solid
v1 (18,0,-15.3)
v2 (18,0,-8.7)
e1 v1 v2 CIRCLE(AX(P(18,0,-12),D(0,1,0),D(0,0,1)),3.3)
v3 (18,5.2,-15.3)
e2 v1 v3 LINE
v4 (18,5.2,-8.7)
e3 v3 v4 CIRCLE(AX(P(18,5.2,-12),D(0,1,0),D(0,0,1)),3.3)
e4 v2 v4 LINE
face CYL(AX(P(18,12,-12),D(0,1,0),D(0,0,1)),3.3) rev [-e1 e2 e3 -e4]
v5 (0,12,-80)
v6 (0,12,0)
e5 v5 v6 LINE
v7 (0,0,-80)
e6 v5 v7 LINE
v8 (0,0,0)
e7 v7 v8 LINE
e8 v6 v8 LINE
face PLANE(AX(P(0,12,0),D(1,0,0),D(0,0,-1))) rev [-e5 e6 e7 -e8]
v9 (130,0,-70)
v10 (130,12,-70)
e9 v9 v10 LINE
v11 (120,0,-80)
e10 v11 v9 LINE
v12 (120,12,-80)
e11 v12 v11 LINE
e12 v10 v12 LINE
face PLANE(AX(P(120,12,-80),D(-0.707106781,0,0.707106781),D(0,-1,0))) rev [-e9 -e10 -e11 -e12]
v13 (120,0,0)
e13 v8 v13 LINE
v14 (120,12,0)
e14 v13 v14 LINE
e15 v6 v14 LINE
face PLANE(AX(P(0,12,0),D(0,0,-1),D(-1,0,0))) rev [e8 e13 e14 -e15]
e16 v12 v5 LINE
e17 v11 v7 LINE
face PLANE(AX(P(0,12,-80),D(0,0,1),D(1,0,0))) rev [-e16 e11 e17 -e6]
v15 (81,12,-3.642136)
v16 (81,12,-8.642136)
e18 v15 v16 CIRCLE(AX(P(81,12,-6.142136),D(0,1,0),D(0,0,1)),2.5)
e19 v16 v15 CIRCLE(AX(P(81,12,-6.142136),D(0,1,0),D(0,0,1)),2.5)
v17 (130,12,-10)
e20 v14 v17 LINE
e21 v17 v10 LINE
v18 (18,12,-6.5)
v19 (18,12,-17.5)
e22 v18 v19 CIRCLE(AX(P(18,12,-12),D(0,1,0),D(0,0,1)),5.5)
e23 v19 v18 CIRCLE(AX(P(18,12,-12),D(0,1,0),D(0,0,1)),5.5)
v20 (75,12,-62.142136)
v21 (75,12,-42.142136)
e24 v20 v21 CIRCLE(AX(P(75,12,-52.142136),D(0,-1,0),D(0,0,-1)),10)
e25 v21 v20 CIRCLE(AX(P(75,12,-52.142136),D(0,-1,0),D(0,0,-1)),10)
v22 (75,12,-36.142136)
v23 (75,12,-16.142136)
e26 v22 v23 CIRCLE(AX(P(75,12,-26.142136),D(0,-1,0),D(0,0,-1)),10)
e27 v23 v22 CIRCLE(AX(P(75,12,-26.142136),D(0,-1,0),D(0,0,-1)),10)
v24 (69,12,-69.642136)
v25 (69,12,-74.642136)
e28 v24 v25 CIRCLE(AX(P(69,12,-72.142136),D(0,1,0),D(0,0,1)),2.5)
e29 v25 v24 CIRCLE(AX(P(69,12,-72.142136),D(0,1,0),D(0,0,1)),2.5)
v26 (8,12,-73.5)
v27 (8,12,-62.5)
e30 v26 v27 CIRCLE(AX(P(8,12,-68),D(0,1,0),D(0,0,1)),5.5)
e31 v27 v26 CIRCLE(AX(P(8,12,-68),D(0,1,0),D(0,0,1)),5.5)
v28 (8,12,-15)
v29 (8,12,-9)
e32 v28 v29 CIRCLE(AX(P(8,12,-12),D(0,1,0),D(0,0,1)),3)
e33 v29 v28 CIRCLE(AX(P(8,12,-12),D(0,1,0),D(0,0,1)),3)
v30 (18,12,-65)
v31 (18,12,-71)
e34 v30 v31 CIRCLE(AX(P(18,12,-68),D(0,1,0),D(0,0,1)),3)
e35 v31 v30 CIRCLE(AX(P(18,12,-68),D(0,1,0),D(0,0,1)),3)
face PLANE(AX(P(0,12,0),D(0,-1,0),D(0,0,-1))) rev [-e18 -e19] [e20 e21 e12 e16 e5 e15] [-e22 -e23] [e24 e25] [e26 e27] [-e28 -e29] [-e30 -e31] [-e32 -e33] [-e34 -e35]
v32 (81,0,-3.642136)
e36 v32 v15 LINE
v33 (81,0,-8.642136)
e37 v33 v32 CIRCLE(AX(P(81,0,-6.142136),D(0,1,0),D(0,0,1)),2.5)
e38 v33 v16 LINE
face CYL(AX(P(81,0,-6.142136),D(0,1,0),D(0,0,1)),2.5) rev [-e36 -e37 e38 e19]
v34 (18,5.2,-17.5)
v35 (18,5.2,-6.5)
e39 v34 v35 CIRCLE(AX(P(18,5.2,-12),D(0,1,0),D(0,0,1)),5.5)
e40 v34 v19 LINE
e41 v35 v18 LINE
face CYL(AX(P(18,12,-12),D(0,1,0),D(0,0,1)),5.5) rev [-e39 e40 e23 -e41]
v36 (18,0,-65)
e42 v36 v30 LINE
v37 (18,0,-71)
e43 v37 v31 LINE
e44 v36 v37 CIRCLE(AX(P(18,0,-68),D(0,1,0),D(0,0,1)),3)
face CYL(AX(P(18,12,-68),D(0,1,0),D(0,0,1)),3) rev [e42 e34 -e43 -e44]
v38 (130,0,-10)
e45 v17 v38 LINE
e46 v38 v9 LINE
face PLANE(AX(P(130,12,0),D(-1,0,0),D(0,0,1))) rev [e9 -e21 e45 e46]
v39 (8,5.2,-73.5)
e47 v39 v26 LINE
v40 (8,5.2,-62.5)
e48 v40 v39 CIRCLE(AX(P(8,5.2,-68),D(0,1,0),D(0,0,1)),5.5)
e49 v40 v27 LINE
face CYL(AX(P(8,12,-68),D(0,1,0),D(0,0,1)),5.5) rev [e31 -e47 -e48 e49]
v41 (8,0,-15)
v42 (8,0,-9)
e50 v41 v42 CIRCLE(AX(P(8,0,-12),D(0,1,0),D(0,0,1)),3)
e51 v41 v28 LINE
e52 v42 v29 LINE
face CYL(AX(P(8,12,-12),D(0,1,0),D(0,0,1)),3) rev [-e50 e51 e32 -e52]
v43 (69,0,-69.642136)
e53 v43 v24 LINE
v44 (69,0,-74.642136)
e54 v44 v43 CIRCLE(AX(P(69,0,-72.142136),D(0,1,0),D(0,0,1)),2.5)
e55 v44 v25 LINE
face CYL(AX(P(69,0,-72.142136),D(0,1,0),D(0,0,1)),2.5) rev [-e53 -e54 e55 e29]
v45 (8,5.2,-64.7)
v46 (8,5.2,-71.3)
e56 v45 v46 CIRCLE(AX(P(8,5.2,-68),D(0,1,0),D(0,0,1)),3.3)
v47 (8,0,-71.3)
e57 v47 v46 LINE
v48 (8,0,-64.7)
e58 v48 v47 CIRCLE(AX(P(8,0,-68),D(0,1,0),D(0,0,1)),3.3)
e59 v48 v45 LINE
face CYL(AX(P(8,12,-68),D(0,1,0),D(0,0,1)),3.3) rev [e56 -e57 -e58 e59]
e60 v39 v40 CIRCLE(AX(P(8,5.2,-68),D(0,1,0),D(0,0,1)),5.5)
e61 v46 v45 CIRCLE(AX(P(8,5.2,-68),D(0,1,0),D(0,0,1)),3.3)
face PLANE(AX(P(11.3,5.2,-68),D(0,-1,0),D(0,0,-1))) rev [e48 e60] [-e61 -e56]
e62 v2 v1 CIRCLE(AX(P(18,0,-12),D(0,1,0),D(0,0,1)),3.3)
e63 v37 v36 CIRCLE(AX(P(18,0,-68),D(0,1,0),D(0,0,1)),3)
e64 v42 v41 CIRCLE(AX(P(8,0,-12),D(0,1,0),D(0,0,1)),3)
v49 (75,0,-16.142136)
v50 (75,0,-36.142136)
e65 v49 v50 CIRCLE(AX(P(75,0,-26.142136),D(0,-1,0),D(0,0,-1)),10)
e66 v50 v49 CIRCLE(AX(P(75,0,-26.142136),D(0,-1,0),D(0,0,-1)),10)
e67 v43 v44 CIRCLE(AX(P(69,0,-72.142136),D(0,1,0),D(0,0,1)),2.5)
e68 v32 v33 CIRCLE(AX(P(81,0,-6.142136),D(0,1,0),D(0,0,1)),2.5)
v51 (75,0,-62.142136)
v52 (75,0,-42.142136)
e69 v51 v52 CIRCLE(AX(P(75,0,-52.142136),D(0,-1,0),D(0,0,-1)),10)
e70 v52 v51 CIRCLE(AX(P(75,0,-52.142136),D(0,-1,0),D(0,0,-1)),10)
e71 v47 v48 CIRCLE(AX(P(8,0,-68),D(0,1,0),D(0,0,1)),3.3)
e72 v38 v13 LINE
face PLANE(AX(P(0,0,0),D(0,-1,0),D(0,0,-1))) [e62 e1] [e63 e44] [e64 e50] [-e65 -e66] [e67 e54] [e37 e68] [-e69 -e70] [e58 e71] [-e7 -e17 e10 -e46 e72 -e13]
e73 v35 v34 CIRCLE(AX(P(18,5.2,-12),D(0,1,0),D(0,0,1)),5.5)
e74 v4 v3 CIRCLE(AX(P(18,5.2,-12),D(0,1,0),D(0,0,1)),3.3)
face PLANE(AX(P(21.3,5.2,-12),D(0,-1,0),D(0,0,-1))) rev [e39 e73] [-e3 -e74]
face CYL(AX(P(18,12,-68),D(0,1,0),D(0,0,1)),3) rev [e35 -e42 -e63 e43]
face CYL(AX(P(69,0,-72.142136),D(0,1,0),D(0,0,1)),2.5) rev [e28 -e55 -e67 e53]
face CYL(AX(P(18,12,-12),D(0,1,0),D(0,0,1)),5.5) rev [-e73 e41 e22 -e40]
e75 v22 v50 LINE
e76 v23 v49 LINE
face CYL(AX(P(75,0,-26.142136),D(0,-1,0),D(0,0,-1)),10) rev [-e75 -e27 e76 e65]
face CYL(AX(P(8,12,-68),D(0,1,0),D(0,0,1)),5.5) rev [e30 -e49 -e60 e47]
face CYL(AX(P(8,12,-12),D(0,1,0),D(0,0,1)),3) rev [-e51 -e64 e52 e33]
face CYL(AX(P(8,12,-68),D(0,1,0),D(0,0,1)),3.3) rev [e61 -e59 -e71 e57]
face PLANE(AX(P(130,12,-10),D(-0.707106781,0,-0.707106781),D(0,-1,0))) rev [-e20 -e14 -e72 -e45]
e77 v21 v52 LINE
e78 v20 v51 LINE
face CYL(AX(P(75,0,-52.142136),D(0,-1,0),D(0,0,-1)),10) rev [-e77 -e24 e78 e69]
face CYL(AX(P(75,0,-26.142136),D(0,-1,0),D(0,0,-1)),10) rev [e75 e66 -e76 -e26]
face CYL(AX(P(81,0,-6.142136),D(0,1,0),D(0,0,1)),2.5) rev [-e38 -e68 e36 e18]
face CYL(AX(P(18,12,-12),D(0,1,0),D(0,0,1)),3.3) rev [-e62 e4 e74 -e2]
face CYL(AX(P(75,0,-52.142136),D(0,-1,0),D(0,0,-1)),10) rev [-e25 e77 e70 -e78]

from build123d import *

# Parameters (mm, degrees)
SKETCH1_W                                            = 130
SKETCH1_H                                            = 80
BOSS_EXTRUDE1_DEPTH                                  = 12
CHAMFER1_SIZE                                        = 10
CBORE_FOR_M6_HEXAGON_SOCKET_HEAD_CAP_SCR_D           = 6.6
CBORE_FOR_M6_HEXAGON_SOCKET_HEAD_CAP_SCR_CBORE_D     = 11
CBORE_FOR_M6_HEXAGON_SOCKET_HEAD_CAP_SCR_CBORE_DEPTH = 6.8
F_6_0MM_DOWEL_HOLE_1_D                               = 6
F_20_0MM_DOWEL_HOLE_1_D                              = 20
SKETCH17_R                                           = 2.5
CUT_EXTRUDE1_DEPTH                                   = 154.114336363


with BuildPart() as part:
    # Sketch1 → Boss-Extrude1 (new body)
    with BuildSketch(Plane(origin=(0, 0, 0), x_dir=(1, 0, 0), z_dir=(0, 1, 0))):
        with Locations((65, 40)):
            Rectangle(SKETCH1_W, SKETCH1_H)
    extrude(amount=BOSS_EXTRUDE1_DEPTH)

    # Chamfer1
    chamfer1_edges = [part.edges().sort_by_distance(p)[0] for p in [
        (130, 6, -80),
        (130, 6, 0),
    ]]
    chamfer(chamfer1_edges, length=CHAMFER1_SIZE)

    # CBORE for M6 Hexagon socket head cap screws1 (through all)
    with Locations(Plane(origin=(8, 12, -68), x_dir=(0, 0, 1), z_dir=(0, 1, 0))):
        with Locations((0, 0), (56, 10)):
            CounterBoreHole(CBORE_FOR_M6_HEXAGON_SOCKET_HEAD_CAP_SCR_D / 2, CBORE_FOR_M6_HEXAGON_SOCKET_HEAD_CAP_SCR_CBORE_D / 2, CBORE_FOR_M6_HEXAGON_SOCKET_HEAD_CAP_SCR_CBORE_DEPTH)

    # Ø6.0mm dowel hole 1 (through all)
    with Locations(Plane(origin=(18, 12, -68), x_dir=(0, 0, 1), z_dir=(0, 1, 0))):
        with Locations((0, 0), (56, -10)):
            Hole(F_6_0MM_DOWEL_HOLE_1_D / 2)

    # Ø20.0mm dowel hole 1 (through all)
    with Locations(Plane(origin=(0, 0, 0), x_dir=(-1, 0, 0), z_dir=(0, -1, 0))):
        with Locations((-75, 52.142135624), (-75, 26.142135624)):
            Hole(F_20_0MM_DOWEL_HOLE_1_D / 2)

    # Sketch17 → Cut-Extrude1 (cut, through all)
    with BuildSketch(Plane(origin=(0, 12, 0), x_dir=(1, 0, 0), z_dir=(0, 1, 0))):
        with Locations(Location((81, 6.142135624, 0), (0, 0, 270))):
            Circle(SKETCH17_R)
        with Locations(Location((69, 72.142135624, 0), (0, 0, 270))):
            Circle(SKETCH17_R)
    extrude(amount=-CUT_EXTRUDE1_DEPTH, mode=Mode.SUBTRACT)


solid = part.part
